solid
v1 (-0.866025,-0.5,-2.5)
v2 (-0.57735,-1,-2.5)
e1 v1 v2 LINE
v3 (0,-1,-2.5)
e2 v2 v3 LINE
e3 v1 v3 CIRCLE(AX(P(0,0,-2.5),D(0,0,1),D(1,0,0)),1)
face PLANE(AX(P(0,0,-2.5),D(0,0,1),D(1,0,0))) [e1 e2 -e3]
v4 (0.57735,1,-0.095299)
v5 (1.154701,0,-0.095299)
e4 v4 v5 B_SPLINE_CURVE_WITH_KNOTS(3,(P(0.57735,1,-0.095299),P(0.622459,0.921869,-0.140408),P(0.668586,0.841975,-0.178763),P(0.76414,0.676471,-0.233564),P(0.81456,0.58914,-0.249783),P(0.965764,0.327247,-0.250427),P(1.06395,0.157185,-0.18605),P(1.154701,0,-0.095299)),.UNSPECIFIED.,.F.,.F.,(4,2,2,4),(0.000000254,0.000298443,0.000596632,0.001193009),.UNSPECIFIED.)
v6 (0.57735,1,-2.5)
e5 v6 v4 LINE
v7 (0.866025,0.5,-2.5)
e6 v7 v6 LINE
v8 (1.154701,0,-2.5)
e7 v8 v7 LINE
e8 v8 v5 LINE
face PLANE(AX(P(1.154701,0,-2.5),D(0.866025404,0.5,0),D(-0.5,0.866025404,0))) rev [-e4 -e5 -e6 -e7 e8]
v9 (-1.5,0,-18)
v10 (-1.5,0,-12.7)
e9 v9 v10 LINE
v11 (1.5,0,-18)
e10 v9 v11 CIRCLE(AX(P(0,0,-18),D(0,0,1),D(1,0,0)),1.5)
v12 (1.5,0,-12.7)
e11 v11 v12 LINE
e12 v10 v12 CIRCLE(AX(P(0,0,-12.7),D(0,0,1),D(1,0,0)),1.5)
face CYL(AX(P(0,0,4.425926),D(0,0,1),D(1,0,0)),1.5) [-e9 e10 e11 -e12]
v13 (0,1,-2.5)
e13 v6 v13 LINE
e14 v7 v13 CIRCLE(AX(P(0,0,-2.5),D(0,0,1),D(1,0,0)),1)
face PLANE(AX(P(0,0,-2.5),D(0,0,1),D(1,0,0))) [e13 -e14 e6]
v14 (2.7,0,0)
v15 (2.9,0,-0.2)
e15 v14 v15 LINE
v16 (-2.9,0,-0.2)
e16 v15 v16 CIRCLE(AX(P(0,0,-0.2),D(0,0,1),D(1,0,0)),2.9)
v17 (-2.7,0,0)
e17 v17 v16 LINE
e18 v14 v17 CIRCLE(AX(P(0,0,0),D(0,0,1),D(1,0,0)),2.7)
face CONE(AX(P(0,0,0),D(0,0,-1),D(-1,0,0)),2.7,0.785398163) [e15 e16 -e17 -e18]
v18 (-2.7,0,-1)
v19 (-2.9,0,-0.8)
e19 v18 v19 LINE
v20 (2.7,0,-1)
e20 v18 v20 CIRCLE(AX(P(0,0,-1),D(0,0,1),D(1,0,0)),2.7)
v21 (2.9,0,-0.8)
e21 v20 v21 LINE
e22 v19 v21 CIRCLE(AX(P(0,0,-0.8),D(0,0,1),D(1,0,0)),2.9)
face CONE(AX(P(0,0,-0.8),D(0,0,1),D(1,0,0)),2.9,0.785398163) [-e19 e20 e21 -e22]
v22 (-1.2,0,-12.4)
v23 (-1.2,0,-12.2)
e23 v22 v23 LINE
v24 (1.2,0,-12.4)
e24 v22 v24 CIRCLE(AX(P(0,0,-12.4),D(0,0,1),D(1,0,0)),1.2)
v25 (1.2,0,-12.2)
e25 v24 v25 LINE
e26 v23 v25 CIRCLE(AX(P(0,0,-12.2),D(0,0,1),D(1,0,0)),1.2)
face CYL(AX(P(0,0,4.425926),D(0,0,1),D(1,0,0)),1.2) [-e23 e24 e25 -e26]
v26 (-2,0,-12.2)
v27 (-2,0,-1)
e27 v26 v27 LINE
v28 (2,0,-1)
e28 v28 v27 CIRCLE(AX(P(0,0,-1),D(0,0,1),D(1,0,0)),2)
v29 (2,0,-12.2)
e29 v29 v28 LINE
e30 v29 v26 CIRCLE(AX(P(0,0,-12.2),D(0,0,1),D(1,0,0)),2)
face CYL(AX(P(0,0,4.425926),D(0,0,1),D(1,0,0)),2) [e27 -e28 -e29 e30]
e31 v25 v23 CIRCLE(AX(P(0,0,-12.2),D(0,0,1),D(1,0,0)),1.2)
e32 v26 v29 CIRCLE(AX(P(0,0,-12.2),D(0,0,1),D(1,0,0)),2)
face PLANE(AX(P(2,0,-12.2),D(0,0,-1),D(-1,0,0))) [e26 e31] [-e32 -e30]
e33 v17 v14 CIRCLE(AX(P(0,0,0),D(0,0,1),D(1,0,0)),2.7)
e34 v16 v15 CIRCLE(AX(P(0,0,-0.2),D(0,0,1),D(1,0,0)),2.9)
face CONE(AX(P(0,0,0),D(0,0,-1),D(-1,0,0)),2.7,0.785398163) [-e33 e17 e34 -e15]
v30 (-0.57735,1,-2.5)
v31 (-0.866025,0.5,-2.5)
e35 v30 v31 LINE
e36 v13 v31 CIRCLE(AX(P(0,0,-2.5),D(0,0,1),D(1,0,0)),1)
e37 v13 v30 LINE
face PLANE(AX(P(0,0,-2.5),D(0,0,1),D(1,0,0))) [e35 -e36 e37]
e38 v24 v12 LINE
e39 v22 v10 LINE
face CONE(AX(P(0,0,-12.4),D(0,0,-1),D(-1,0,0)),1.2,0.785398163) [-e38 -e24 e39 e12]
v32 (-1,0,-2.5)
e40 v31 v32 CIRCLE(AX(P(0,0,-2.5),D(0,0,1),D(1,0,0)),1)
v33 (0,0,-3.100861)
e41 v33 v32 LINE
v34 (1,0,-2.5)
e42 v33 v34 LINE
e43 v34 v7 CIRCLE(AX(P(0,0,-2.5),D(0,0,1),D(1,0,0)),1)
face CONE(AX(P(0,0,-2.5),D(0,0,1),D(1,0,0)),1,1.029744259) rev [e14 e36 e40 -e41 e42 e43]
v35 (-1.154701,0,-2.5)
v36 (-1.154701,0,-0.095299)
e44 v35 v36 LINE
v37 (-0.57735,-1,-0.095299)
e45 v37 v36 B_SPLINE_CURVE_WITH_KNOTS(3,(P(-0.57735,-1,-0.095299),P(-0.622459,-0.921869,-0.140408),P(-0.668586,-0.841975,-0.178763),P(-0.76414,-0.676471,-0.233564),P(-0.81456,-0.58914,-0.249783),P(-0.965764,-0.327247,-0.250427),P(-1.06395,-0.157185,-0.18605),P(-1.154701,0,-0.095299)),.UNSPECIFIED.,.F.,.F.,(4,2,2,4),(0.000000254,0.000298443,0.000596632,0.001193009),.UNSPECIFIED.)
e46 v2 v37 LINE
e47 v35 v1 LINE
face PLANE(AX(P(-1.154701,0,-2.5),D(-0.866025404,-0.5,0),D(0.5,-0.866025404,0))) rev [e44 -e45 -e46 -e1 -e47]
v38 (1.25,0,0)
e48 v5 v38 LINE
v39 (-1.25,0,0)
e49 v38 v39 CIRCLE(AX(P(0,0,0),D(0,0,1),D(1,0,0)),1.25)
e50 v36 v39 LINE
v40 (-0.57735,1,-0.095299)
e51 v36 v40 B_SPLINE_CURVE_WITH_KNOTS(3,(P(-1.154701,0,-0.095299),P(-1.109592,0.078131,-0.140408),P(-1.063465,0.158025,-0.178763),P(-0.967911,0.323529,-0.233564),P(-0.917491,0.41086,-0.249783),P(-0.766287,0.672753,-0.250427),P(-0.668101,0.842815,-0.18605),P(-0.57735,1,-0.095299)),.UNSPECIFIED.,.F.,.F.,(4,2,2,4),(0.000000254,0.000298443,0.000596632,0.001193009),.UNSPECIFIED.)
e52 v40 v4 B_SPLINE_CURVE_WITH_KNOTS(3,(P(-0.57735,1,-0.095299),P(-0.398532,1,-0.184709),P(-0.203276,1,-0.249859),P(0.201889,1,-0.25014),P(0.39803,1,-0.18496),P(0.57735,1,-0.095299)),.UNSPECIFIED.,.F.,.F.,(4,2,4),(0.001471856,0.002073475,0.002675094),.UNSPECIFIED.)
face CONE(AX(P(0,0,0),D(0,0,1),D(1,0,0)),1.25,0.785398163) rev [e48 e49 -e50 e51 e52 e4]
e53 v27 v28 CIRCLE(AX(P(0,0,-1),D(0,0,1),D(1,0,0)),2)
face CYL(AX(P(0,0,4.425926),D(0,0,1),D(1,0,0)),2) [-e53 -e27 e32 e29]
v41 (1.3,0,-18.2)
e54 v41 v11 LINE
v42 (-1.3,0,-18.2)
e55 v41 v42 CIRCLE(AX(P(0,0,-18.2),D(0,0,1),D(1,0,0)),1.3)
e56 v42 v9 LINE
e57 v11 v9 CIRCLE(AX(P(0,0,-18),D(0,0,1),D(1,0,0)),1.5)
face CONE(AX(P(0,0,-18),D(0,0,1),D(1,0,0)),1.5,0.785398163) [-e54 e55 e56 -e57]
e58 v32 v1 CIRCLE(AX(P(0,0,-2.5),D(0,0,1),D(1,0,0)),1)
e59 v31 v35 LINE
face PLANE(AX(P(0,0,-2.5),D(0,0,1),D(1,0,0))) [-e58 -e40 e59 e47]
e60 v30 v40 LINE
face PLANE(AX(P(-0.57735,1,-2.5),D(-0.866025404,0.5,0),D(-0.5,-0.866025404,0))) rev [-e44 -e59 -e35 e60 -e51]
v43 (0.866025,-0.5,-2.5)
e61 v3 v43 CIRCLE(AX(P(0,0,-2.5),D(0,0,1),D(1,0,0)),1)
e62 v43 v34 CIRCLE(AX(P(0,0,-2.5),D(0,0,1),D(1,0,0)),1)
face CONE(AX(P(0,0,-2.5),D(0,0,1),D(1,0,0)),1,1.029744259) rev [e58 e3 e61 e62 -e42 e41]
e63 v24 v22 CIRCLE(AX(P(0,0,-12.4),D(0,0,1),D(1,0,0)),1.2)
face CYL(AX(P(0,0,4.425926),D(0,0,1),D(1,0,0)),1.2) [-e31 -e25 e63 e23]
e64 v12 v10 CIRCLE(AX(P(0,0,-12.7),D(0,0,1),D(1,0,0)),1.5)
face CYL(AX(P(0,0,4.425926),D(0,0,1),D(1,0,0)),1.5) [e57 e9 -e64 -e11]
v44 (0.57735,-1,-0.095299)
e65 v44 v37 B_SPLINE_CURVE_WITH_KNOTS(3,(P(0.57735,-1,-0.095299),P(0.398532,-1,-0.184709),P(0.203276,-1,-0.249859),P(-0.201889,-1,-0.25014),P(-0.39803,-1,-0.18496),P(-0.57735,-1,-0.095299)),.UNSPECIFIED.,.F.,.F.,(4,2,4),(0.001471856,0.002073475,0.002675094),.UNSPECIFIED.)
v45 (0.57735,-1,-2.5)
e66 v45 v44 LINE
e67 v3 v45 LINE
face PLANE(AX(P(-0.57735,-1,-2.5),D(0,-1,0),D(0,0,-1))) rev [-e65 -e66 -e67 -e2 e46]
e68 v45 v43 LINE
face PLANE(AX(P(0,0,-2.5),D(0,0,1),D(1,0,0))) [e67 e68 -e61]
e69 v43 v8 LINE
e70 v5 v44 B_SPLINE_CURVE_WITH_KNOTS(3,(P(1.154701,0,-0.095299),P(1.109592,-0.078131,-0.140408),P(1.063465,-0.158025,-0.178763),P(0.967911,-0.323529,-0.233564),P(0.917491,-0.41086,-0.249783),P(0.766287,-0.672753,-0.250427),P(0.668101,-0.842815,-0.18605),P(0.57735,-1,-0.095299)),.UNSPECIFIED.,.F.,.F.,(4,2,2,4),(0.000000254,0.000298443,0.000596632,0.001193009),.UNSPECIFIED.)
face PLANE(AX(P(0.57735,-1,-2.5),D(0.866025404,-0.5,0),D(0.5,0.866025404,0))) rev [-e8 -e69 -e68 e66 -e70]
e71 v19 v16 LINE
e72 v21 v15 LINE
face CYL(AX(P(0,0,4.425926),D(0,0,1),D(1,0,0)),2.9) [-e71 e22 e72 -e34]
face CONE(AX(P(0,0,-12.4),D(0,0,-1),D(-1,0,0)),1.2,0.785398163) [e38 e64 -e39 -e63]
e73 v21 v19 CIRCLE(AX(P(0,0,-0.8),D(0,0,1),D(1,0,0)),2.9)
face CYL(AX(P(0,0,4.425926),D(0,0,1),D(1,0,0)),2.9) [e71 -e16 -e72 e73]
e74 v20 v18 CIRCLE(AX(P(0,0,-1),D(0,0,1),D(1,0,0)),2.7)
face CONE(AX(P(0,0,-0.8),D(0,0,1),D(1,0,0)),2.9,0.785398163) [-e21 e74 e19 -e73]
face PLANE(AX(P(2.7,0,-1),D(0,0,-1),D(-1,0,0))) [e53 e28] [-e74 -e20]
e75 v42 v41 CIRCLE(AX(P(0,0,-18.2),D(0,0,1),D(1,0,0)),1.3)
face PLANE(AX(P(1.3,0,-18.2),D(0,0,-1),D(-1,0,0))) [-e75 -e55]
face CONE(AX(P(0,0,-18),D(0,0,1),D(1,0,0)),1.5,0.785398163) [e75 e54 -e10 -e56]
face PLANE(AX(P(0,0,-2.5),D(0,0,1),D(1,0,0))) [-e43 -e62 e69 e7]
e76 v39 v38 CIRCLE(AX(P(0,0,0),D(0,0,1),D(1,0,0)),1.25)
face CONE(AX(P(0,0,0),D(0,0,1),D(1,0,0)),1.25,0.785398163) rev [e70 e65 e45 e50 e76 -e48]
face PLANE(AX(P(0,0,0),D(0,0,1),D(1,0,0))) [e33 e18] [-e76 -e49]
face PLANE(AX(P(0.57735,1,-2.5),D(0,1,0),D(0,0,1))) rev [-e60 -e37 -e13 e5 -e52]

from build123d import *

# Parameters (mm, degrees)
SIZE_MM_DOWEL_HOLE1_D           = 2
SIZE_MM_DOWEL_HOLE1_DEPTH       = 2.5
SIZE_MM_DOWEL_HOLE1_CSINK_D     = 2.5
SIZE_MM_DOWEL_HOLE1_CSINK_ANGLE = 90
SIZE_MM_DOWEL_HOLE1_TIP         = 0.600860619
CUT_EXTRUDE1_DEPTH              = 2.5


with BuildPart() as part:
    # Sketch2 → Revolve1 (revolve)
    with BuildSketch(Plane(origin=(0, 0, 0), x_dir=(1, 0, 0), z_dir=(0, 1, 0))):
        Polygon((0, 0), (2.7, 0), (2.9, 0.2), (2.9, 0.8), (2.7, 1), (2, 1), (2, 12.2), (1.2, 12.2), (1.2, 12.4), (1.5, 12.7), (1.5, 18), (1.3, 18.2), (0, 18.2), align=None)
    revolve(axis=Axis((0, 0, 4.425925926), (0, 0, -1)))

    # Size mm Dowel Hole1
    with Locations(Plane.XY):
        with Locations((0, 0)):
            CounterSinkHole(SIZE_MM_DOWEL_HOLE1_D / 2, SIZE_MM_DOWEL_HOLE1_CSINK_D / 2, depth=SIZE_MM_DOWEL_HOLE1_DEPTH, counter_sink_angle=SIZE_MM_DOWEL_HOLE1_CSINK_ANGLE)
            with Locations((0, 0, -(SIZE_MM_DOWEL_HOLE1_DEPTH + SIZE_MM_DOWEL_HOLE1_TIP / 2))):  # 118° drill point
                Cone(0, SIZE_MM_DOWEL_HOLE1_D / 2, SIZE_MM_DOWEL_HOLE1_TIP, mode=Mode.SUBTRACT)

    # Sketch5 → Cut-Extrude1 (cut)
    with BuildSketch(Plane.XY):
        Polygon((0.577350269, -1), (1.154700538, 0), (0.577350269, 1), (-0.577350269, 1), (-1.154700538, 0), (-0.577350269, -1), align=None)
    extrude(amount=-CUT_EXTRUDE1_DEPTH, mode=Mode.SUBTRACT)


solid = part.part
